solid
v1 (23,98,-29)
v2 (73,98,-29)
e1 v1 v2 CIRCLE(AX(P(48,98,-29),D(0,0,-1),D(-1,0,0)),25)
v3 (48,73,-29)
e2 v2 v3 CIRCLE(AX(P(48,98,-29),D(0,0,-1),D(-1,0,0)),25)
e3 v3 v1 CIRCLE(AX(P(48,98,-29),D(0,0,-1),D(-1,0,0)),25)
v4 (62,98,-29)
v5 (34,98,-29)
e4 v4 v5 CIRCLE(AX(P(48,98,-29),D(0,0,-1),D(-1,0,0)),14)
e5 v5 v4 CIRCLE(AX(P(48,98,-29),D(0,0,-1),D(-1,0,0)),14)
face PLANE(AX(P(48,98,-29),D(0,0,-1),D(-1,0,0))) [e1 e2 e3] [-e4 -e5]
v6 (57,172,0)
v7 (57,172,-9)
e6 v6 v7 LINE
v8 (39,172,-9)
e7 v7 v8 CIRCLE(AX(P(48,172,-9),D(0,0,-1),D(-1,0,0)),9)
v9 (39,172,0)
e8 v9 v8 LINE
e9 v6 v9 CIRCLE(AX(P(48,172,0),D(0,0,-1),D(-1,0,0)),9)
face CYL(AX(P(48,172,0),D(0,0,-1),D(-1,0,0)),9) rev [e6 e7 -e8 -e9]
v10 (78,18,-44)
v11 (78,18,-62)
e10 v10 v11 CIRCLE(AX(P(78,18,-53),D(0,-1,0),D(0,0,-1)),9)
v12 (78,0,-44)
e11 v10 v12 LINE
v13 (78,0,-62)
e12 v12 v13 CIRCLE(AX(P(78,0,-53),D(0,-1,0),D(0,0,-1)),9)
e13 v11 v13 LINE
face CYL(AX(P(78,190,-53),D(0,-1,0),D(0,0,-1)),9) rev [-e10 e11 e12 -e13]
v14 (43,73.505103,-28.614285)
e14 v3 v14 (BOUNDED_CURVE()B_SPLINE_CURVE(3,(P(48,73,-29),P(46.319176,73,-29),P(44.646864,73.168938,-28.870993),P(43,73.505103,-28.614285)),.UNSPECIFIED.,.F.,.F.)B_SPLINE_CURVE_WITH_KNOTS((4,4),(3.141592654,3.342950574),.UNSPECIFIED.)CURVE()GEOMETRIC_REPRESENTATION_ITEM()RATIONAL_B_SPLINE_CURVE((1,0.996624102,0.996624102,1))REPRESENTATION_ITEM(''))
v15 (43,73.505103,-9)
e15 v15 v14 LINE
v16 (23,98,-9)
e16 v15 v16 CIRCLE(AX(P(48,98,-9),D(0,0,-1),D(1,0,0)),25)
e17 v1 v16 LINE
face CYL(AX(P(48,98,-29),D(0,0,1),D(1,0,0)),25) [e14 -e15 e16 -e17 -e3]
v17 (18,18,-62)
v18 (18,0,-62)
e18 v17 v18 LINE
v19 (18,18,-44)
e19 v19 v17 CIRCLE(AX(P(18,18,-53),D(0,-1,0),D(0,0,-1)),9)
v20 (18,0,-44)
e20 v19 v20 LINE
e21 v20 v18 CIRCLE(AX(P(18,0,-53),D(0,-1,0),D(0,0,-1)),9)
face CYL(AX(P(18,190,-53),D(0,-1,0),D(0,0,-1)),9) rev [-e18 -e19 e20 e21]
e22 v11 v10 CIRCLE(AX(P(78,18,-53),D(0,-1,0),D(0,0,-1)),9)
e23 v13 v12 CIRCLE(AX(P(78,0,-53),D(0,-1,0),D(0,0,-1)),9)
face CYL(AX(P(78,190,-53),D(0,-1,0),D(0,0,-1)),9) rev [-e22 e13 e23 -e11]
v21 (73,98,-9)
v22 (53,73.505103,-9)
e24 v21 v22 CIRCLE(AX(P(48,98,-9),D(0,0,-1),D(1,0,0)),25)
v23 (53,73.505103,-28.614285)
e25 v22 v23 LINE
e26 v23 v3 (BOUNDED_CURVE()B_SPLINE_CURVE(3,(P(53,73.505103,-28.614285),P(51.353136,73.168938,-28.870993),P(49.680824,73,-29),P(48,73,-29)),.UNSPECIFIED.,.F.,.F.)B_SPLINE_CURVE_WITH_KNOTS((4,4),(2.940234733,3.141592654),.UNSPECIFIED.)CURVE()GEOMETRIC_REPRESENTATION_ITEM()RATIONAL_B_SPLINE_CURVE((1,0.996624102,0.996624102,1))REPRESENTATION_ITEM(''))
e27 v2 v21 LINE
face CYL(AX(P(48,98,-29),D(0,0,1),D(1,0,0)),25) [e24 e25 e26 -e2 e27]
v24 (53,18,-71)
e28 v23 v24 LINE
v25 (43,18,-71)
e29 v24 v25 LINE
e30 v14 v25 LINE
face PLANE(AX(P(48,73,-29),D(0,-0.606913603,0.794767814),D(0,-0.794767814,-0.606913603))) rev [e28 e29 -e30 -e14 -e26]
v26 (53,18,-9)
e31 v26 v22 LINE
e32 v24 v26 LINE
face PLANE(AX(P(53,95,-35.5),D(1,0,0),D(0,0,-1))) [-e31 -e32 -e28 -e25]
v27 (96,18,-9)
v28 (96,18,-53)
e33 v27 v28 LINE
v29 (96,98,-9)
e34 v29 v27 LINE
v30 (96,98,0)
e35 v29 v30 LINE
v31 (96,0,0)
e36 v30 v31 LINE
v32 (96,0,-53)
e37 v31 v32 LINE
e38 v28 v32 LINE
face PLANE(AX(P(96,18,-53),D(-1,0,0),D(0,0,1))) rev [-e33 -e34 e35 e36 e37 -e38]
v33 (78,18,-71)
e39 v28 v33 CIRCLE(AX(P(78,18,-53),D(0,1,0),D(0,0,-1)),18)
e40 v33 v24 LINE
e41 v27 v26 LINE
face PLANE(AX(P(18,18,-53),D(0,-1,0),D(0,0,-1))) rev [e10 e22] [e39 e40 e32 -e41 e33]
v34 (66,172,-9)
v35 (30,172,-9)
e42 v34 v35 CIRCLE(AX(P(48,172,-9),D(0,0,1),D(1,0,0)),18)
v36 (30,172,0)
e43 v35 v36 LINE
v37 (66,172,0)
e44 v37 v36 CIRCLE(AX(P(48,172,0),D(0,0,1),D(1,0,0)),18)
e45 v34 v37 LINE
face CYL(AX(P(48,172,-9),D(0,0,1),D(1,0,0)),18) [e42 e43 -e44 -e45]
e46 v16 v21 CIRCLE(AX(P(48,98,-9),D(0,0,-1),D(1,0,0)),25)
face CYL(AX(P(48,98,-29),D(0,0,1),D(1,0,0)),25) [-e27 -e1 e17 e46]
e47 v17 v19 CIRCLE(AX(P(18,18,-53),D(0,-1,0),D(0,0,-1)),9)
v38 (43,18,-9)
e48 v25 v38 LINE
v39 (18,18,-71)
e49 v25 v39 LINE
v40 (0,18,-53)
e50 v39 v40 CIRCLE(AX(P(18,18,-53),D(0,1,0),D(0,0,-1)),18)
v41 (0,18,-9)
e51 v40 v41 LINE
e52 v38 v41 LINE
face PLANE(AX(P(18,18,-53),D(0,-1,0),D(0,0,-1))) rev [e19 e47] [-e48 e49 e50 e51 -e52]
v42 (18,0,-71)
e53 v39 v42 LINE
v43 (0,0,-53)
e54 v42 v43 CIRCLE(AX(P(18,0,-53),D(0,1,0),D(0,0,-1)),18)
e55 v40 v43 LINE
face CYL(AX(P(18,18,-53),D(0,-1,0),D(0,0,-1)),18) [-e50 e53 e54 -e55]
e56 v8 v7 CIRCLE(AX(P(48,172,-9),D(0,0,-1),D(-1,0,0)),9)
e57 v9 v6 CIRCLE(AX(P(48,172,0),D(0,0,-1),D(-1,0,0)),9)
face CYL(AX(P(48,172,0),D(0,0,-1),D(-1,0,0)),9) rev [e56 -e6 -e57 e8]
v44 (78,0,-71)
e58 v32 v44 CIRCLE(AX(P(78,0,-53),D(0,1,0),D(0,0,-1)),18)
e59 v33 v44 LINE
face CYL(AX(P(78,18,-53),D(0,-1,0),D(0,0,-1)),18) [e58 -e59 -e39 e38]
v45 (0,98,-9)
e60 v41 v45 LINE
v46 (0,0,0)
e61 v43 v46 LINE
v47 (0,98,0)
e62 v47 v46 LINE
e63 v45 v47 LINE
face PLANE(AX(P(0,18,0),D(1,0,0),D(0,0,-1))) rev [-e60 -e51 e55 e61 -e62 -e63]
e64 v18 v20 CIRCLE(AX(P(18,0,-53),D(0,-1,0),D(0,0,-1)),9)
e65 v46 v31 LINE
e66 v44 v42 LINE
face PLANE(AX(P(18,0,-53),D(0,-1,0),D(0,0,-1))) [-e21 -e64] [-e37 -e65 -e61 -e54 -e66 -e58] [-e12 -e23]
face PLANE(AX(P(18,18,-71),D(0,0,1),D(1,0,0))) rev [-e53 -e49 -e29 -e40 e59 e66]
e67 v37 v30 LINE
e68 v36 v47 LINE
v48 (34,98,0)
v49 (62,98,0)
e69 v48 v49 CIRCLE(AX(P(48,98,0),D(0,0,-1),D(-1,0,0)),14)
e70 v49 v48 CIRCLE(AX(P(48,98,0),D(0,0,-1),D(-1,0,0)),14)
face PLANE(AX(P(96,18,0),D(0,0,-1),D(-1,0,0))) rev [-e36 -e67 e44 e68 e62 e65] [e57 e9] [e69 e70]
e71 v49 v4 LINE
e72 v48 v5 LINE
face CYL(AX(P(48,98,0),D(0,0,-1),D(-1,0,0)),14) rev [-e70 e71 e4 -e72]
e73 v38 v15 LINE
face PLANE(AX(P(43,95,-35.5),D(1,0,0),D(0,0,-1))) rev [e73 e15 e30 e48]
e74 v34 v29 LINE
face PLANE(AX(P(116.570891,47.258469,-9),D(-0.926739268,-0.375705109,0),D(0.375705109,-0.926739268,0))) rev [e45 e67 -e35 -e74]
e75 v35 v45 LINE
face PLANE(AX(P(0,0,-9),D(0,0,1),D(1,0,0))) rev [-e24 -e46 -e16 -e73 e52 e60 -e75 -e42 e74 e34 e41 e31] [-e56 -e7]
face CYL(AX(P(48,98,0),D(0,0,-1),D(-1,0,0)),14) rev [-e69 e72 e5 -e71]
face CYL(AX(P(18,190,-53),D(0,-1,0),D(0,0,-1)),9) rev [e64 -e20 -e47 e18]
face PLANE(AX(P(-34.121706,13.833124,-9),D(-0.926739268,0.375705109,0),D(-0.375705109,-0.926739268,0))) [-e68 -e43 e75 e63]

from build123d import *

# Parameters (mm, degrees)
BASE_PLATE_DEPTH          = 18
UPRIGHT_PLATE_DEPTH       = 9
UPRIGHT_TOP_HOLE_SKETCH_R = 9
UPRIGHT_TOP_HOLE_18_DEPTH = 9
HUB_BOSS_SKETCH_R         = 25
HUB_BOSS_DEPTH            = 20
HUB_BORE_SKETCH_R         = 14
HUB_BORE_28_DEPTH         = 217.979261682
BASE_HOLE_SKETCH_R        = 9
BASE_HOLE_18_DEPTH        = 225.403654159
SUPPORT_RIB_REACH         = 210.435
SUPPORT_RIB_SKETCH_WALL_W = 488.071885176
SUPPORT_RIB_SKETCH_WALL_H = 10


with BuildPart() as part:
    # Base Plate Sketch → Base Plate (new body)
    with BuildSketch(Plane(origin=(0, 0, 0), x_dir=(1, 0, 0), z_dir=(0, 1, 0))):
        with BuildLine():
            Line((0, 0), (0, 53))
            ThreePointArc((0, 53), (5.272077939, 65.727922061), (18, 71))
            Line((18, 71), (78, 71))
            ThreePointArc((78, 71), (90.727922061, 65.727922061), (96, 53))
            Line((96, 53), (96, 0))
            Line((96, 0), (0, 0))
        make_face()
    extrude(amount=BASE_PLATE_DEPTH)

    # Upright Plate Sketch → Upright Plate (add)
    with BuildSketch(Plane.XY):
        with BuildLine():
            Line((0, 98), (0, 18))
            Line((0, 18), (96, 18))
            Line((96, 18), (96, 98))
            Line((96, 98), (66, 172))
            ThreePointArc((66, 172), (48, 190), (30, 172))
            Line((30, 172), (0, 98))
        make_face()
    extrude(amount=-UPRIGHT_PLATE_DEPTH)

    # Upright Top Hole Sketch → Upright Top Hole Ø18 (cut)
    with BuildSketch(Plane(origin=(0, 0, -9), x_dir=(-1, 0, 0), z_dir=(0, 0, -1))):
        with Locations((-48, 172)):
            Circle(UPRIGHT_TOP_HOLE_SKETCH_R)
    extrude(amount=-UPRIGHT_TOP_HOLE_18_DEPTH, mode=Mode.SUBTRACT)

    # Hub Boss Sketch → Hub Boss (add)
    with BuildSketch(Plane(origin=(0, 0, -9), x_dir=(-1, 0, 0), z_dir=(0, 0, -1))):
        with Locations(Location((-48, 98, 0), (0, 0, 180))):
            Circle(HUB_BOSS_SKETCH_R)
    extrude(amount=HUB_BOSS_DEPTH)

    # Hub Bore Sketch → Hub Bore Ø28 (cut, through all)
    with BuildSketch(Plane(origin=(0, 0, -29), x_dir=(-1, 0, 0), z_dir=(0, 0, -1))):
        with Locations((-48, 98)):
            Circle(HUB_BORE_SKETCH_R)
    extrude(amount=-HUB_BORE_28_DEPTH, mode=Mode.SUBTRACT)

    # Base Hole Sketch → Base Hole Ø18 (cut, through all)
    with BuildSketch(Plane.XZ):
        with Locations(Location((18, -53, 0), (0, 0, 270))):
            Circle(BASE_HOLE_SKETCH_R)
        with Locations(Location((78, -53, 0), (0, 0, 270))):
            Circle(BASE_HOLE_SKETCH_R)
    extrude(amount=-BASE_HOLE_18_DEPTH, mode=Mode.SUBTRACT)

    # Support Rib Sketch wall → Support Rib (add, up to next)
    with BuildSketch(Plane(origin=(48, 45.5, -50), x_dir=(0, -0.794767813927, -0.606913603362), z_dir=(0, 0.606913603362, -0.794767813927)), mode=Mode.PRIVATE) as support_rib_sk1:
        Rectangle(SUPPORT_RIB_SKETCH_WALL_W, SUPPORT_RIB_SKETCH_WALL_H)
    support_rib_tool1 = extrude(support_rib_sk1.sketch, amount=-SUPPORT_RIB_REACH, mode=Mode.PRIVATE) - part.part
    add(support_rib_tool1.solids().sort_by_distance((48, 45.5, -50))[0])


solid = part.part
